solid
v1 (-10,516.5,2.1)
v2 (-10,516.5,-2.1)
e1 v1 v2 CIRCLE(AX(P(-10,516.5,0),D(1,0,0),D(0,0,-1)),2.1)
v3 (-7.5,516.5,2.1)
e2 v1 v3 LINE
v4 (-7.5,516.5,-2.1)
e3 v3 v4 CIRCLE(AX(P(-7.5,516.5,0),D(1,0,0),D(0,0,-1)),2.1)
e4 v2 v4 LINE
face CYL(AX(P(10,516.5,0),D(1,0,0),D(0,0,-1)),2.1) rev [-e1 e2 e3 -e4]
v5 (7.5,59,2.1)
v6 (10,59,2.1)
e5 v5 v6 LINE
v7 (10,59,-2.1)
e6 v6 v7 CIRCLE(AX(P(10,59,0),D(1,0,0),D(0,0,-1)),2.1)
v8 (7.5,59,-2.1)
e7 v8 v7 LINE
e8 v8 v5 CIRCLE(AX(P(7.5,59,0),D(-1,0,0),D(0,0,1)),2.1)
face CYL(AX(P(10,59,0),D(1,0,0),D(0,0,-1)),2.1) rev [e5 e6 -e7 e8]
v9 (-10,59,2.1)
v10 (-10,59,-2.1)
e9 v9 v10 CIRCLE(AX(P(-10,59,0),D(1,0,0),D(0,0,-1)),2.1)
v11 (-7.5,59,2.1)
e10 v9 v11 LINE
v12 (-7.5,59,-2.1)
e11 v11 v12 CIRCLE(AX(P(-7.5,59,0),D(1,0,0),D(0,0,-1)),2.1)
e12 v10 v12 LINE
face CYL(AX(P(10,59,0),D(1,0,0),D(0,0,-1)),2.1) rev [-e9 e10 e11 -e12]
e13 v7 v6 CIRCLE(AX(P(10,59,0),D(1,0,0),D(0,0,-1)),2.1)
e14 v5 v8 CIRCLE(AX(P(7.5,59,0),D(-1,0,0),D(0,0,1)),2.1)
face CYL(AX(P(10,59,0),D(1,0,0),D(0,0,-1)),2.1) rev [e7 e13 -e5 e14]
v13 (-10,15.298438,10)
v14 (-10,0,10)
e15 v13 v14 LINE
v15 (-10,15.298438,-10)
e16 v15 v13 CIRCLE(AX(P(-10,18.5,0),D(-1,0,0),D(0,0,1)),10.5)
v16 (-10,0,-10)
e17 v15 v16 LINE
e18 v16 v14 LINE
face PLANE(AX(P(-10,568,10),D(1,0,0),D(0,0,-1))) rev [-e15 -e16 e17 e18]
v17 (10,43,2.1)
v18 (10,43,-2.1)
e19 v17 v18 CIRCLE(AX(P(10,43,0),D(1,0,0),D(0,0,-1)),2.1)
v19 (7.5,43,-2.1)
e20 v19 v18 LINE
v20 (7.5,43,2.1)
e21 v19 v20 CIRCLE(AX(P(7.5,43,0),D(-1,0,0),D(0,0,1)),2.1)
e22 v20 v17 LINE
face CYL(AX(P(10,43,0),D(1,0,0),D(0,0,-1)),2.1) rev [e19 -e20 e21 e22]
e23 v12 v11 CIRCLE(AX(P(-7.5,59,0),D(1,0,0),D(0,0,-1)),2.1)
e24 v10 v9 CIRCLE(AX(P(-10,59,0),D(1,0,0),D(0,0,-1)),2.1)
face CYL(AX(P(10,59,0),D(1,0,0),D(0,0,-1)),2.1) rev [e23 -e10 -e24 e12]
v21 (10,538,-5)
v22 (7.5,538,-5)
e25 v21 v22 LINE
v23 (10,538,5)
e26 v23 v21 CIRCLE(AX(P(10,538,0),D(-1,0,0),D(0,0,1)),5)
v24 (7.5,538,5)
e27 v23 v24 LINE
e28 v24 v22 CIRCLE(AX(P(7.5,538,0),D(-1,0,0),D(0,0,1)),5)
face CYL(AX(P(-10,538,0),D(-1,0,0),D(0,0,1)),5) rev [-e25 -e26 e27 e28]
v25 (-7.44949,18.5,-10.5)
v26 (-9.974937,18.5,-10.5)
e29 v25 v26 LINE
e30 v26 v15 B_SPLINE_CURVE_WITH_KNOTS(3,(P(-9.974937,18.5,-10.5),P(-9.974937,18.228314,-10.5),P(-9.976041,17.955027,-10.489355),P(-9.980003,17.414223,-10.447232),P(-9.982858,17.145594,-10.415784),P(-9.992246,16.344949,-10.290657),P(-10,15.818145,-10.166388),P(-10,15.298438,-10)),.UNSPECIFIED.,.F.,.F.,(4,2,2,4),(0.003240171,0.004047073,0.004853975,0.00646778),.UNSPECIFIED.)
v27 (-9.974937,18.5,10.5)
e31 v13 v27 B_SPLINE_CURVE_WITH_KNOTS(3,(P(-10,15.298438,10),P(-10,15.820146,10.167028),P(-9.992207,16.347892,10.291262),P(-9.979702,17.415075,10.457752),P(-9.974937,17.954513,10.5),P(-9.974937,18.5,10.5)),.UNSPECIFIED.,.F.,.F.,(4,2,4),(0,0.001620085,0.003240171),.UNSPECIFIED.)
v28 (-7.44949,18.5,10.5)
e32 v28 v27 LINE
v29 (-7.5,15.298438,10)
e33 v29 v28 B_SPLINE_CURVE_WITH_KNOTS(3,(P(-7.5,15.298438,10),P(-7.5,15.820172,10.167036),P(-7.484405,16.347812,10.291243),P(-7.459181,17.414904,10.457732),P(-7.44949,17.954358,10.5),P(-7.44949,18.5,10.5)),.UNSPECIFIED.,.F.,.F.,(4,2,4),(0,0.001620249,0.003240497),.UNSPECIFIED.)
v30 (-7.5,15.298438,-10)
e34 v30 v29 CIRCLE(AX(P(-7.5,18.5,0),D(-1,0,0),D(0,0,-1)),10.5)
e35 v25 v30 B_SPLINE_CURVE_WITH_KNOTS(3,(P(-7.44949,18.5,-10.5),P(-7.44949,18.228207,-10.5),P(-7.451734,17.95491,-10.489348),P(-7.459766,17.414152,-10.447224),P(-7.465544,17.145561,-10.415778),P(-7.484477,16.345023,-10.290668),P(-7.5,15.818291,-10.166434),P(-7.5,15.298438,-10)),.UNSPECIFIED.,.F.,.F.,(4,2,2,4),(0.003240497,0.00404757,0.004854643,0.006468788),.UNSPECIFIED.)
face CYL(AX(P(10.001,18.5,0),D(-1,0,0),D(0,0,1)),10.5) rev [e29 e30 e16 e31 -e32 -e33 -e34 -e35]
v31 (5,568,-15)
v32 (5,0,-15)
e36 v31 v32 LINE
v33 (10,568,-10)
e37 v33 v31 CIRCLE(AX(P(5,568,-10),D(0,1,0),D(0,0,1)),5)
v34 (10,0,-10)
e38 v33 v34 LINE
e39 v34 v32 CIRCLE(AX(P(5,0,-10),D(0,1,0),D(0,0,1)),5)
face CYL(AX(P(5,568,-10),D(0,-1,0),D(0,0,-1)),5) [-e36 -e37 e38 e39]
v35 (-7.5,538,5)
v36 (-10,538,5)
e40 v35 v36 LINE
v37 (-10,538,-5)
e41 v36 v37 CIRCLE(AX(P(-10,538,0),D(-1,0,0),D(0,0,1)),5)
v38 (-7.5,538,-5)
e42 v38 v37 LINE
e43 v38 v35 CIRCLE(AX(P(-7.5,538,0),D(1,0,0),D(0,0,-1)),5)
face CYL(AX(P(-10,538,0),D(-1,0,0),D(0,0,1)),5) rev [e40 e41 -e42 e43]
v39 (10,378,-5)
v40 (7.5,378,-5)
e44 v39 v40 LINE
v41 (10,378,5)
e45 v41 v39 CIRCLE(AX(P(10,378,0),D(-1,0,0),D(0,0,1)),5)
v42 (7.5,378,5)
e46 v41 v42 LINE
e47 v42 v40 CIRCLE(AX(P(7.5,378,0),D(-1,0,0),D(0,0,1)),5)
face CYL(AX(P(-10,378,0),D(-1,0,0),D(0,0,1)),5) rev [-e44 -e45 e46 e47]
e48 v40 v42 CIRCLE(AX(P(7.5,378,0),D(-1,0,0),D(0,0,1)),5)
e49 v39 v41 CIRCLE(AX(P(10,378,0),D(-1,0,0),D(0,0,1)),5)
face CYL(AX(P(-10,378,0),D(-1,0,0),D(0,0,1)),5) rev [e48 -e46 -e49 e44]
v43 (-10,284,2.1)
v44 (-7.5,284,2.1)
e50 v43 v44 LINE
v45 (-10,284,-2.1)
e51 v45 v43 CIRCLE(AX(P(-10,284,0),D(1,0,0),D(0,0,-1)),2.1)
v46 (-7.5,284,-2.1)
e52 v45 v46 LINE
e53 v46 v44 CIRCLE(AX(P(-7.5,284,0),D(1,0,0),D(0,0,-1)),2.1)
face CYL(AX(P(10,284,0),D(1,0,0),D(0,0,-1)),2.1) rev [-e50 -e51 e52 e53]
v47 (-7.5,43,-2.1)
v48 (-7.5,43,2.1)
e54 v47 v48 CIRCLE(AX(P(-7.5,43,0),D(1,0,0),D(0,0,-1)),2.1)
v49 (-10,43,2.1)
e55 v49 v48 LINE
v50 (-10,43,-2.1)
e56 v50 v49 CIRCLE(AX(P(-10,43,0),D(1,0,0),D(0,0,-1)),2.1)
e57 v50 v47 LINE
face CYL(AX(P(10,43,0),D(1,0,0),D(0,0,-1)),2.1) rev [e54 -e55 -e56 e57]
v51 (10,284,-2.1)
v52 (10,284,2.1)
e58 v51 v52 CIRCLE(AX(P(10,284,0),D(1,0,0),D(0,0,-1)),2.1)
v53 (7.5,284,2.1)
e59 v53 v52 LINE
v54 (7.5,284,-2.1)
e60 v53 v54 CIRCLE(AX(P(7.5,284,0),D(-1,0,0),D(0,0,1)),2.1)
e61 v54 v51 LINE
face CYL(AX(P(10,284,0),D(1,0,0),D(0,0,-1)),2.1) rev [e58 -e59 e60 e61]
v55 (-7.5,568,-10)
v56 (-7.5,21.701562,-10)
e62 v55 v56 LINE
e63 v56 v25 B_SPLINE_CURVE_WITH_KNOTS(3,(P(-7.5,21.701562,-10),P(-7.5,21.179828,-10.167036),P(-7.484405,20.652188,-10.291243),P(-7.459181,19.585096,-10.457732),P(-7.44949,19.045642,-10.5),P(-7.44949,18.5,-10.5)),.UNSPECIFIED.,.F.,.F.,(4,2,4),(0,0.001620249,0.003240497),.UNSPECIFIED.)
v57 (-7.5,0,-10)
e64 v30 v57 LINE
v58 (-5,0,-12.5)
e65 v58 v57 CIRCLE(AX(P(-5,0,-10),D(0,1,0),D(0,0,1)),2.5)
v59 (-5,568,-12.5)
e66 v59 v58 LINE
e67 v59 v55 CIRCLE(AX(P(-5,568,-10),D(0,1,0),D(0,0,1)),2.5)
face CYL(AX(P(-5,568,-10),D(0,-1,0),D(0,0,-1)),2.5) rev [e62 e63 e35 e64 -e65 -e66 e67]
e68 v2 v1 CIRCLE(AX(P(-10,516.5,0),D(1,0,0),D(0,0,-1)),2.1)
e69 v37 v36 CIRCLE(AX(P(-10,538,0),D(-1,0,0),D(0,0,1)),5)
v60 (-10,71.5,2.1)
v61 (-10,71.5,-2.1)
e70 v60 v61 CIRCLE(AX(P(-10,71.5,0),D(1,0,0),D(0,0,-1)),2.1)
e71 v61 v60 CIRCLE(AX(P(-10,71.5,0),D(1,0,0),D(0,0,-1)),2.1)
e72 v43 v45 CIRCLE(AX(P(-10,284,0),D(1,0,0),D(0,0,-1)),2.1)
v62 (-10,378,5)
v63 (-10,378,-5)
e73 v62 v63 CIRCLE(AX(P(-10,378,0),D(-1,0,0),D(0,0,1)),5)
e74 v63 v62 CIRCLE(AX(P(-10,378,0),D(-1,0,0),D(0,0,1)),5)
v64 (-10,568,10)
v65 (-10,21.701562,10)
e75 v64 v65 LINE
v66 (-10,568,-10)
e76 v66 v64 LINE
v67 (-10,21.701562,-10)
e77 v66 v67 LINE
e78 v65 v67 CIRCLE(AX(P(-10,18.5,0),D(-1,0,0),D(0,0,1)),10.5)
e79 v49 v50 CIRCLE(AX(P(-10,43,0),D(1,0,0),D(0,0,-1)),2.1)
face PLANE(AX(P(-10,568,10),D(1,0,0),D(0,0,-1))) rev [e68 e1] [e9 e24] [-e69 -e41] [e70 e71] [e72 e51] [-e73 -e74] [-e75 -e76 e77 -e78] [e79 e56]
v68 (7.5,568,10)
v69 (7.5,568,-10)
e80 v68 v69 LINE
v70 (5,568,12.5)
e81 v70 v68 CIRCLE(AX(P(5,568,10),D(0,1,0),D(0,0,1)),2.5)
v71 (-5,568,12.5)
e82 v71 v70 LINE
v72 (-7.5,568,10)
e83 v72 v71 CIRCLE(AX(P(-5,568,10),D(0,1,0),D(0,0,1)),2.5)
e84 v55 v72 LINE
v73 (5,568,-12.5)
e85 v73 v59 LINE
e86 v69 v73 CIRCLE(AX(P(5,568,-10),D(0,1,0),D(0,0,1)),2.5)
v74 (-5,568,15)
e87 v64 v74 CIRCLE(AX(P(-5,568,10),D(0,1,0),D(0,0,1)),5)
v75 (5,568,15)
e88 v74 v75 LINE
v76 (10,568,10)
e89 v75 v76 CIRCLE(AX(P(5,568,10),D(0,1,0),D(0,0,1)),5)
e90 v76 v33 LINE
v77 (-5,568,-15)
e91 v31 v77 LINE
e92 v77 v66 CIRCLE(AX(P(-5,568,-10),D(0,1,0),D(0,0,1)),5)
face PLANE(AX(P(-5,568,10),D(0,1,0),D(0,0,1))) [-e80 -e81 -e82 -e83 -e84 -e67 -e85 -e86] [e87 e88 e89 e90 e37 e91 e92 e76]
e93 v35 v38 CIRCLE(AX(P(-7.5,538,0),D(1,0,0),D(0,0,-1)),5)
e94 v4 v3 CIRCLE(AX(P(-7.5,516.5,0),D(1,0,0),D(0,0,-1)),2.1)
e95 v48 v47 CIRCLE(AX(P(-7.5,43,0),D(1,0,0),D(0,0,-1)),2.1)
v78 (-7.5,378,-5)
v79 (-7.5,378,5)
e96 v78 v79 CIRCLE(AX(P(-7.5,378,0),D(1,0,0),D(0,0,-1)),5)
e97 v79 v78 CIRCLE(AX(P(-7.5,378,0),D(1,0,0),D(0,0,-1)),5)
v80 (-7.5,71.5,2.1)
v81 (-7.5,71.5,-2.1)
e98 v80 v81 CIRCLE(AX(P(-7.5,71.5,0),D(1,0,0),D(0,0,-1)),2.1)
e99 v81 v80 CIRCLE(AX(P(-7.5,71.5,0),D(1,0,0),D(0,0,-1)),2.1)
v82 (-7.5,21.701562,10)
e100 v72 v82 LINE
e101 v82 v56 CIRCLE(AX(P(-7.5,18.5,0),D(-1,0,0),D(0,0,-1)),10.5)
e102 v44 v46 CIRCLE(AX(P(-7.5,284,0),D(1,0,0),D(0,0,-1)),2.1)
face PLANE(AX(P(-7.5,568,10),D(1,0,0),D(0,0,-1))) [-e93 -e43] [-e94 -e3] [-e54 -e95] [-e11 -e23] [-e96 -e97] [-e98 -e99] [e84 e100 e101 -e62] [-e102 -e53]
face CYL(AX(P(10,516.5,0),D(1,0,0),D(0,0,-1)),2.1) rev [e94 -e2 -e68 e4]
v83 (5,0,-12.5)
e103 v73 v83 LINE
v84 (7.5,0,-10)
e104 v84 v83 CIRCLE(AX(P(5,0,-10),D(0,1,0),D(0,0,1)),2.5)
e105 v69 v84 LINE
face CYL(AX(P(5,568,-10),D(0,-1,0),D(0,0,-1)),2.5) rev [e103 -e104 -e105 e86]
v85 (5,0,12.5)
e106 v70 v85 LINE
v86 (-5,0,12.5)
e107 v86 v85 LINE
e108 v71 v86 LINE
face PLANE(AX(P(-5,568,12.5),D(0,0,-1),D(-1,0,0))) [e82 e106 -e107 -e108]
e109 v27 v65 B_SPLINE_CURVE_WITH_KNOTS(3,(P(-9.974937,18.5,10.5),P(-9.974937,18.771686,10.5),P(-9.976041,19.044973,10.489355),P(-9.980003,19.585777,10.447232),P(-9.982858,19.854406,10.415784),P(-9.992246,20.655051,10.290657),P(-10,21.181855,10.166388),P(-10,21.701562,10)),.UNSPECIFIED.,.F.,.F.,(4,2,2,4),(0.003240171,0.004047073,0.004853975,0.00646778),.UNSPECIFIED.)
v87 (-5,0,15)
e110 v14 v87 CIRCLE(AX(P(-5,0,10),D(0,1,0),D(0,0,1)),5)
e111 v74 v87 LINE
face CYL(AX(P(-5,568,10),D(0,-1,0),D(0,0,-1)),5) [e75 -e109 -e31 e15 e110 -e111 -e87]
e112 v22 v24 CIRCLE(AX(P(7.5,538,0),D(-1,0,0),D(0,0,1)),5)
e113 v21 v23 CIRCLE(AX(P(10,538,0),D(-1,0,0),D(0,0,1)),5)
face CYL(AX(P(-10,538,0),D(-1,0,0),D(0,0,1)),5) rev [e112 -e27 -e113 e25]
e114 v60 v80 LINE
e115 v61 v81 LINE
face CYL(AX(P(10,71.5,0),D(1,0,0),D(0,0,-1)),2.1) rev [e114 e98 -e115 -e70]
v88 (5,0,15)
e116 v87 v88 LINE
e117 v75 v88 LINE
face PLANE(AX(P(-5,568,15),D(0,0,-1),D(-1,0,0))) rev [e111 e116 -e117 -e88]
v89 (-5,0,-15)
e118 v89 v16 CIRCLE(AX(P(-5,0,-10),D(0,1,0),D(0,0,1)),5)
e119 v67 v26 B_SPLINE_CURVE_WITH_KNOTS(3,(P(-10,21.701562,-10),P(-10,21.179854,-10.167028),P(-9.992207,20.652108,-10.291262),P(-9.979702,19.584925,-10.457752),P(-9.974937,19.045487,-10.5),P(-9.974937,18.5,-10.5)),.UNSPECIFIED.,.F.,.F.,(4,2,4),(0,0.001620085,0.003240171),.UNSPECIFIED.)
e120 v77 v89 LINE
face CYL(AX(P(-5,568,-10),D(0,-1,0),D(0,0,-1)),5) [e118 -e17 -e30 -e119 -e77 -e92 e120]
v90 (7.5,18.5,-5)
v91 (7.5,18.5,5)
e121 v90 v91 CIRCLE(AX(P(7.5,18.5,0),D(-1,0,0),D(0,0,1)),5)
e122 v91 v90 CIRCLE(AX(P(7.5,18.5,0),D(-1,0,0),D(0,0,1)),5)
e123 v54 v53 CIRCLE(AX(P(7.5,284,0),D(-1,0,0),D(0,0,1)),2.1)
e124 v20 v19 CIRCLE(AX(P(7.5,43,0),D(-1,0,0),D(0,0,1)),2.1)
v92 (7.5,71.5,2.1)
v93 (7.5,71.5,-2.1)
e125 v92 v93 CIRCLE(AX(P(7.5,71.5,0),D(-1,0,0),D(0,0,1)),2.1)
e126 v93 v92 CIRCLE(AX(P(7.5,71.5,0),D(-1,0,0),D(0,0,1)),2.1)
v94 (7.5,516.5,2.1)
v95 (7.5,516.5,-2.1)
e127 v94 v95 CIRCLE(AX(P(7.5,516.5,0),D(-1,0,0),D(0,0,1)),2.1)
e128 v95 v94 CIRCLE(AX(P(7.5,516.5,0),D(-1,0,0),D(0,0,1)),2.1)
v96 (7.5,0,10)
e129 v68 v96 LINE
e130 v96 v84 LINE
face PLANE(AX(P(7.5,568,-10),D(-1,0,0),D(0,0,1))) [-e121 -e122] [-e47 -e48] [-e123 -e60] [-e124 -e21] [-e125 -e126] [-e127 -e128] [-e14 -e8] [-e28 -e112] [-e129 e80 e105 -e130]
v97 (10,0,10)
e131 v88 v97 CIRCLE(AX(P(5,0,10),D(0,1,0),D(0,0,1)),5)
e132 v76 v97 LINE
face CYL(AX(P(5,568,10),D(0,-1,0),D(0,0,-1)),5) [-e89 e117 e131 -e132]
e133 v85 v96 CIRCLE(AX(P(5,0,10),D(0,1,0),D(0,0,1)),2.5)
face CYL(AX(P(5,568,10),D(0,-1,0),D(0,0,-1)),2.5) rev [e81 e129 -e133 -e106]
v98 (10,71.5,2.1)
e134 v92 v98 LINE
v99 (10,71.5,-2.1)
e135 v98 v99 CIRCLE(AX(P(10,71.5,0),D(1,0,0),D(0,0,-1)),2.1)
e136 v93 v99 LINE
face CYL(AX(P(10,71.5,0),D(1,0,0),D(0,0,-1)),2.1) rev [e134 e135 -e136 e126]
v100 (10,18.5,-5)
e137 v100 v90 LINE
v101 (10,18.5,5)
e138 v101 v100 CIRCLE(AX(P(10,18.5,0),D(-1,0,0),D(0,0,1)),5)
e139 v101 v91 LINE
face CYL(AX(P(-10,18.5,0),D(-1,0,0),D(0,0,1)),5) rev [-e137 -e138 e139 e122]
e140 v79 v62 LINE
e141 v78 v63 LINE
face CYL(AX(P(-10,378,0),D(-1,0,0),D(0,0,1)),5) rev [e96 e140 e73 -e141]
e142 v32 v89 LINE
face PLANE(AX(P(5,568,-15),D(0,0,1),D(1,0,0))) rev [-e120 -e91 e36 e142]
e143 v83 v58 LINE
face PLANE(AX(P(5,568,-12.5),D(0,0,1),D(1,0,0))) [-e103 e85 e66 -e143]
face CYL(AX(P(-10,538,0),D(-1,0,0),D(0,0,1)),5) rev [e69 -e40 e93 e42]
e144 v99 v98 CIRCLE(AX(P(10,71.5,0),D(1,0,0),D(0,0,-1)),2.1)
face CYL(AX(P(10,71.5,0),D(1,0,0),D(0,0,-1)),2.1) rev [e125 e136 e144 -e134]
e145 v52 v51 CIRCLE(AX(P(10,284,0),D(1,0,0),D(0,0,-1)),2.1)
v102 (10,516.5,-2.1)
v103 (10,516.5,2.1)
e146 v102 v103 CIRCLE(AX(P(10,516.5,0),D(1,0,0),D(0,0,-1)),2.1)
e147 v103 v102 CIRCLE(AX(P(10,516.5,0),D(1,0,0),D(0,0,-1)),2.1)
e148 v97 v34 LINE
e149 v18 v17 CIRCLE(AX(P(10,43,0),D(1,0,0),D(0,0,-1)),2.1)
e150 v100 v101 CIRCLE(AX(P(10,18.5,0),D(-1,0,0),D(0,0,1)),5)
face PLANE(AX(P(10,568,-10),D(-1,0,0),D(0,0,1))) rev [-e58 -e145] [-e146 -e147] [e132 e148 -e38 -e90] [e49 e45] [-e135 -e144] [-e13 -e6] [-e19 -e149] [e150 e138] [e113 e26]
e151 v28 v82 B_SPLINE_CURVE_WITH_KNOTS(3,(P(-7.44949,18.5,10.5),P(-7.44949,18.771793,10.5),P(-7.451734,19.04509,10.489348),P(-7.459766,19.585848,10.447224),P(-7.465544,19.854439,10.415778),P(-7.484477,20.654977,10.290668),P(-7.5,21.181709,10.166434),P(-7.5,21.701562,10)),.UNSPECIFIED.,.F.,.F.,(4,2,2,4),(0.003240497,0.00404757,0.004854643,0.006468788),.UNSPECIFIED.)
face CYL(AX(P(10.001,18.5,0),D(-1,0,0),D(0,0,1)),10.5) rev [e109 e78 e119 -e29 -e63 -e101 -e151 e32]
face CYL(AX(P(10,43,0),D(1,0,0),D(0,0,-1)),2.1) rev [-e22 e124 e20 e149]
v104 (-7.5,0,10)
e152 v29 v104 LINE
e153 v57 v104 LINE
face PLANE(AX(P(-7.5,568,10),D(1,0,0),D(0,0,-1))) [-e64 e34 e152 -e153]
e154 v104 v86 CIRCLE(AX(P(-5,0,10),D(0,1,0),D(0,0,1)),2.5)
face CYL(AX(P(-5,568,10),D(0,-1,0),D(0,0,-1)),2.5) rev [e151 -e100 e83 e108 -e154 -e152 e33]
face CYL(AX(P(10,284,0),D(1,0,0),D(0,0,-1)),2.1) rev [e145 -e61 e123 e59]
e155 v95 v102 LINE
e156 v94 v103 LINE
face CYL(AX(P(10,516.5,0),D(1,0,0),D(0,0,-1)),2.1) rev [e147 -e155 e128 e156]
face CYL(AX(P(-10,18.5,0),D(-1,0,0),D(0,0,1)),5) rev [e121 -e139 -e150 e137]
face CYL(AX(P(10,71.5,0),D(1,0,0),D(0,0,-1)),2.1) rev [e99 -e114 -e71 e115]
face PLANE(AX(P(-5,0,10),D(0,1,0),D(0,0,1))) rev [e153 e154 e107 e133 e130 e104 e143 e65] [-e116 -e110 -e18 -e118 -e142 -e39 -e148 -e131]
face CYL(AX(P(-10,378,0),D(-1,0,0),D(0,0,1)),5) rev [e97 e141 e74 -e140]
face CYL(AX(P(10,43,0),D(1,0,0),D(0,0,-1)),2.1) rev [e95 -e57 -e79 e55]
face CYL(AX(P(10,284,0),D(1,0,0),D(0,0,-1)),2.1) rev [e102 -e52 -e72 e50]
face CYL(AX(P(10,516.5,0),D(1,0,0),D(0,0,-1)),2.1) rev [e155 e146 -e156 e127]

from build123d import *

# Parameters (mm, degrees)
F_30X20X2_5_1_DEPTH = 568
CUT_EXTRUDE_1_REACH = 570.55
SKETCH_6_R          = 10.5
HOLE_WIZARD_M8_1_D  = 10
HOLE_WIZARD_M5_1_D  = 4.2


with BuildPart() as part:
    # Sketch14 → 矩型管 30X20X2.5(1) (new body)
    with BuildSketch(Plane(origin=(0, 0, 0), x_dir=(-1, 0, 0), z_dir=(0, 1, 0))):
        with BuildLine():
            Line((-5, -15), (5, -15))
            ThreePointArc((5, -15), (8.535533906, -13.535533906), (10, -10))
            Line((10, -10), (10, 10))
            ThreePointArc((10, 10), (8.535533906, 13.535533906), (5, 15))
            Line((5, 15), (-5, 15))
            ThreePointArc((-5, 15), (-8.535533906, 13.535533906), (-10, 10))
            Line((-10, 10), (-10, -10))
            ThreePointArc((-10, -10), (-8.535533906, -13.535533906), (-5, -15))
        make_face()
        with BuildLine():
            Line((-5, -12.5), (5, -12.5))
            ThreePointArc((5, -12.5), (6.767766953, -11.767766953), (7.5, -10))
            Line((7.5, -10), (7.5, 10))
            ThreePointArc((7.5, 10), (6.767766953, 11.767766953), (5, 12.5))
            Line((5, 12.5), (-5, 12.5))
            ThreePointArc((-5, 12.5), (-6.767766953, 11.767766953), (-7.5, 10))
            Line((-7.5, 10), (-7.5, -10))
            ThreePointArc((-7.5, -10), (-6.767766953, -11.767766953), (-5, -12.5))
        make_face(mode=Mode.SUBTRACT)
    extrude(amount=F_30X20X2_5_1_DEPTH)

    # 草图6 → 切除-拉伸1 (cut, up to next)
    with BuildSketch(Plane.ZY.offset(10), mode=Mode.PRIVATE) as cut_extrude_1_sk1:
        with Locations(Location((0, 18.5, 0), (0, 0, 17.752790162))):
            Circle(SKETCH_6_R)
    cut_extrude_1_tool1 = extrude(cut_extrude_1_sk1.sketch, amount=-CUT_EXTRUDE_1_REACH, mode=Mode.PRIVATE) & part.part
    add(cut_extrude_1_tool1.solids().sort_by_distance((-10, 18.5, 0))[0], mode=Mode.SUBTRACT)

    # M8 间隙孔1 (through all)
    with Locations(Plane.ZY.offset(10)):
        with Locations((0, 538), (0, 378), (0, 18.5)):
            Hole(HOLE_WIZARD_M8_1_D / 2)

    # M5 螺纹孔1 (through all)
    with Locations(Plane(origin=(10, 0, 0), x_dir=(0, 0, -1), z_dir=(1, 0, 0))):
        with Locations((0, 516.5), (0, 284), (0, 71.5), (0, 59), (0, 43)):
            Hole(HOLE_WIZARD_M5_1_D / 2)


solid = part.part
